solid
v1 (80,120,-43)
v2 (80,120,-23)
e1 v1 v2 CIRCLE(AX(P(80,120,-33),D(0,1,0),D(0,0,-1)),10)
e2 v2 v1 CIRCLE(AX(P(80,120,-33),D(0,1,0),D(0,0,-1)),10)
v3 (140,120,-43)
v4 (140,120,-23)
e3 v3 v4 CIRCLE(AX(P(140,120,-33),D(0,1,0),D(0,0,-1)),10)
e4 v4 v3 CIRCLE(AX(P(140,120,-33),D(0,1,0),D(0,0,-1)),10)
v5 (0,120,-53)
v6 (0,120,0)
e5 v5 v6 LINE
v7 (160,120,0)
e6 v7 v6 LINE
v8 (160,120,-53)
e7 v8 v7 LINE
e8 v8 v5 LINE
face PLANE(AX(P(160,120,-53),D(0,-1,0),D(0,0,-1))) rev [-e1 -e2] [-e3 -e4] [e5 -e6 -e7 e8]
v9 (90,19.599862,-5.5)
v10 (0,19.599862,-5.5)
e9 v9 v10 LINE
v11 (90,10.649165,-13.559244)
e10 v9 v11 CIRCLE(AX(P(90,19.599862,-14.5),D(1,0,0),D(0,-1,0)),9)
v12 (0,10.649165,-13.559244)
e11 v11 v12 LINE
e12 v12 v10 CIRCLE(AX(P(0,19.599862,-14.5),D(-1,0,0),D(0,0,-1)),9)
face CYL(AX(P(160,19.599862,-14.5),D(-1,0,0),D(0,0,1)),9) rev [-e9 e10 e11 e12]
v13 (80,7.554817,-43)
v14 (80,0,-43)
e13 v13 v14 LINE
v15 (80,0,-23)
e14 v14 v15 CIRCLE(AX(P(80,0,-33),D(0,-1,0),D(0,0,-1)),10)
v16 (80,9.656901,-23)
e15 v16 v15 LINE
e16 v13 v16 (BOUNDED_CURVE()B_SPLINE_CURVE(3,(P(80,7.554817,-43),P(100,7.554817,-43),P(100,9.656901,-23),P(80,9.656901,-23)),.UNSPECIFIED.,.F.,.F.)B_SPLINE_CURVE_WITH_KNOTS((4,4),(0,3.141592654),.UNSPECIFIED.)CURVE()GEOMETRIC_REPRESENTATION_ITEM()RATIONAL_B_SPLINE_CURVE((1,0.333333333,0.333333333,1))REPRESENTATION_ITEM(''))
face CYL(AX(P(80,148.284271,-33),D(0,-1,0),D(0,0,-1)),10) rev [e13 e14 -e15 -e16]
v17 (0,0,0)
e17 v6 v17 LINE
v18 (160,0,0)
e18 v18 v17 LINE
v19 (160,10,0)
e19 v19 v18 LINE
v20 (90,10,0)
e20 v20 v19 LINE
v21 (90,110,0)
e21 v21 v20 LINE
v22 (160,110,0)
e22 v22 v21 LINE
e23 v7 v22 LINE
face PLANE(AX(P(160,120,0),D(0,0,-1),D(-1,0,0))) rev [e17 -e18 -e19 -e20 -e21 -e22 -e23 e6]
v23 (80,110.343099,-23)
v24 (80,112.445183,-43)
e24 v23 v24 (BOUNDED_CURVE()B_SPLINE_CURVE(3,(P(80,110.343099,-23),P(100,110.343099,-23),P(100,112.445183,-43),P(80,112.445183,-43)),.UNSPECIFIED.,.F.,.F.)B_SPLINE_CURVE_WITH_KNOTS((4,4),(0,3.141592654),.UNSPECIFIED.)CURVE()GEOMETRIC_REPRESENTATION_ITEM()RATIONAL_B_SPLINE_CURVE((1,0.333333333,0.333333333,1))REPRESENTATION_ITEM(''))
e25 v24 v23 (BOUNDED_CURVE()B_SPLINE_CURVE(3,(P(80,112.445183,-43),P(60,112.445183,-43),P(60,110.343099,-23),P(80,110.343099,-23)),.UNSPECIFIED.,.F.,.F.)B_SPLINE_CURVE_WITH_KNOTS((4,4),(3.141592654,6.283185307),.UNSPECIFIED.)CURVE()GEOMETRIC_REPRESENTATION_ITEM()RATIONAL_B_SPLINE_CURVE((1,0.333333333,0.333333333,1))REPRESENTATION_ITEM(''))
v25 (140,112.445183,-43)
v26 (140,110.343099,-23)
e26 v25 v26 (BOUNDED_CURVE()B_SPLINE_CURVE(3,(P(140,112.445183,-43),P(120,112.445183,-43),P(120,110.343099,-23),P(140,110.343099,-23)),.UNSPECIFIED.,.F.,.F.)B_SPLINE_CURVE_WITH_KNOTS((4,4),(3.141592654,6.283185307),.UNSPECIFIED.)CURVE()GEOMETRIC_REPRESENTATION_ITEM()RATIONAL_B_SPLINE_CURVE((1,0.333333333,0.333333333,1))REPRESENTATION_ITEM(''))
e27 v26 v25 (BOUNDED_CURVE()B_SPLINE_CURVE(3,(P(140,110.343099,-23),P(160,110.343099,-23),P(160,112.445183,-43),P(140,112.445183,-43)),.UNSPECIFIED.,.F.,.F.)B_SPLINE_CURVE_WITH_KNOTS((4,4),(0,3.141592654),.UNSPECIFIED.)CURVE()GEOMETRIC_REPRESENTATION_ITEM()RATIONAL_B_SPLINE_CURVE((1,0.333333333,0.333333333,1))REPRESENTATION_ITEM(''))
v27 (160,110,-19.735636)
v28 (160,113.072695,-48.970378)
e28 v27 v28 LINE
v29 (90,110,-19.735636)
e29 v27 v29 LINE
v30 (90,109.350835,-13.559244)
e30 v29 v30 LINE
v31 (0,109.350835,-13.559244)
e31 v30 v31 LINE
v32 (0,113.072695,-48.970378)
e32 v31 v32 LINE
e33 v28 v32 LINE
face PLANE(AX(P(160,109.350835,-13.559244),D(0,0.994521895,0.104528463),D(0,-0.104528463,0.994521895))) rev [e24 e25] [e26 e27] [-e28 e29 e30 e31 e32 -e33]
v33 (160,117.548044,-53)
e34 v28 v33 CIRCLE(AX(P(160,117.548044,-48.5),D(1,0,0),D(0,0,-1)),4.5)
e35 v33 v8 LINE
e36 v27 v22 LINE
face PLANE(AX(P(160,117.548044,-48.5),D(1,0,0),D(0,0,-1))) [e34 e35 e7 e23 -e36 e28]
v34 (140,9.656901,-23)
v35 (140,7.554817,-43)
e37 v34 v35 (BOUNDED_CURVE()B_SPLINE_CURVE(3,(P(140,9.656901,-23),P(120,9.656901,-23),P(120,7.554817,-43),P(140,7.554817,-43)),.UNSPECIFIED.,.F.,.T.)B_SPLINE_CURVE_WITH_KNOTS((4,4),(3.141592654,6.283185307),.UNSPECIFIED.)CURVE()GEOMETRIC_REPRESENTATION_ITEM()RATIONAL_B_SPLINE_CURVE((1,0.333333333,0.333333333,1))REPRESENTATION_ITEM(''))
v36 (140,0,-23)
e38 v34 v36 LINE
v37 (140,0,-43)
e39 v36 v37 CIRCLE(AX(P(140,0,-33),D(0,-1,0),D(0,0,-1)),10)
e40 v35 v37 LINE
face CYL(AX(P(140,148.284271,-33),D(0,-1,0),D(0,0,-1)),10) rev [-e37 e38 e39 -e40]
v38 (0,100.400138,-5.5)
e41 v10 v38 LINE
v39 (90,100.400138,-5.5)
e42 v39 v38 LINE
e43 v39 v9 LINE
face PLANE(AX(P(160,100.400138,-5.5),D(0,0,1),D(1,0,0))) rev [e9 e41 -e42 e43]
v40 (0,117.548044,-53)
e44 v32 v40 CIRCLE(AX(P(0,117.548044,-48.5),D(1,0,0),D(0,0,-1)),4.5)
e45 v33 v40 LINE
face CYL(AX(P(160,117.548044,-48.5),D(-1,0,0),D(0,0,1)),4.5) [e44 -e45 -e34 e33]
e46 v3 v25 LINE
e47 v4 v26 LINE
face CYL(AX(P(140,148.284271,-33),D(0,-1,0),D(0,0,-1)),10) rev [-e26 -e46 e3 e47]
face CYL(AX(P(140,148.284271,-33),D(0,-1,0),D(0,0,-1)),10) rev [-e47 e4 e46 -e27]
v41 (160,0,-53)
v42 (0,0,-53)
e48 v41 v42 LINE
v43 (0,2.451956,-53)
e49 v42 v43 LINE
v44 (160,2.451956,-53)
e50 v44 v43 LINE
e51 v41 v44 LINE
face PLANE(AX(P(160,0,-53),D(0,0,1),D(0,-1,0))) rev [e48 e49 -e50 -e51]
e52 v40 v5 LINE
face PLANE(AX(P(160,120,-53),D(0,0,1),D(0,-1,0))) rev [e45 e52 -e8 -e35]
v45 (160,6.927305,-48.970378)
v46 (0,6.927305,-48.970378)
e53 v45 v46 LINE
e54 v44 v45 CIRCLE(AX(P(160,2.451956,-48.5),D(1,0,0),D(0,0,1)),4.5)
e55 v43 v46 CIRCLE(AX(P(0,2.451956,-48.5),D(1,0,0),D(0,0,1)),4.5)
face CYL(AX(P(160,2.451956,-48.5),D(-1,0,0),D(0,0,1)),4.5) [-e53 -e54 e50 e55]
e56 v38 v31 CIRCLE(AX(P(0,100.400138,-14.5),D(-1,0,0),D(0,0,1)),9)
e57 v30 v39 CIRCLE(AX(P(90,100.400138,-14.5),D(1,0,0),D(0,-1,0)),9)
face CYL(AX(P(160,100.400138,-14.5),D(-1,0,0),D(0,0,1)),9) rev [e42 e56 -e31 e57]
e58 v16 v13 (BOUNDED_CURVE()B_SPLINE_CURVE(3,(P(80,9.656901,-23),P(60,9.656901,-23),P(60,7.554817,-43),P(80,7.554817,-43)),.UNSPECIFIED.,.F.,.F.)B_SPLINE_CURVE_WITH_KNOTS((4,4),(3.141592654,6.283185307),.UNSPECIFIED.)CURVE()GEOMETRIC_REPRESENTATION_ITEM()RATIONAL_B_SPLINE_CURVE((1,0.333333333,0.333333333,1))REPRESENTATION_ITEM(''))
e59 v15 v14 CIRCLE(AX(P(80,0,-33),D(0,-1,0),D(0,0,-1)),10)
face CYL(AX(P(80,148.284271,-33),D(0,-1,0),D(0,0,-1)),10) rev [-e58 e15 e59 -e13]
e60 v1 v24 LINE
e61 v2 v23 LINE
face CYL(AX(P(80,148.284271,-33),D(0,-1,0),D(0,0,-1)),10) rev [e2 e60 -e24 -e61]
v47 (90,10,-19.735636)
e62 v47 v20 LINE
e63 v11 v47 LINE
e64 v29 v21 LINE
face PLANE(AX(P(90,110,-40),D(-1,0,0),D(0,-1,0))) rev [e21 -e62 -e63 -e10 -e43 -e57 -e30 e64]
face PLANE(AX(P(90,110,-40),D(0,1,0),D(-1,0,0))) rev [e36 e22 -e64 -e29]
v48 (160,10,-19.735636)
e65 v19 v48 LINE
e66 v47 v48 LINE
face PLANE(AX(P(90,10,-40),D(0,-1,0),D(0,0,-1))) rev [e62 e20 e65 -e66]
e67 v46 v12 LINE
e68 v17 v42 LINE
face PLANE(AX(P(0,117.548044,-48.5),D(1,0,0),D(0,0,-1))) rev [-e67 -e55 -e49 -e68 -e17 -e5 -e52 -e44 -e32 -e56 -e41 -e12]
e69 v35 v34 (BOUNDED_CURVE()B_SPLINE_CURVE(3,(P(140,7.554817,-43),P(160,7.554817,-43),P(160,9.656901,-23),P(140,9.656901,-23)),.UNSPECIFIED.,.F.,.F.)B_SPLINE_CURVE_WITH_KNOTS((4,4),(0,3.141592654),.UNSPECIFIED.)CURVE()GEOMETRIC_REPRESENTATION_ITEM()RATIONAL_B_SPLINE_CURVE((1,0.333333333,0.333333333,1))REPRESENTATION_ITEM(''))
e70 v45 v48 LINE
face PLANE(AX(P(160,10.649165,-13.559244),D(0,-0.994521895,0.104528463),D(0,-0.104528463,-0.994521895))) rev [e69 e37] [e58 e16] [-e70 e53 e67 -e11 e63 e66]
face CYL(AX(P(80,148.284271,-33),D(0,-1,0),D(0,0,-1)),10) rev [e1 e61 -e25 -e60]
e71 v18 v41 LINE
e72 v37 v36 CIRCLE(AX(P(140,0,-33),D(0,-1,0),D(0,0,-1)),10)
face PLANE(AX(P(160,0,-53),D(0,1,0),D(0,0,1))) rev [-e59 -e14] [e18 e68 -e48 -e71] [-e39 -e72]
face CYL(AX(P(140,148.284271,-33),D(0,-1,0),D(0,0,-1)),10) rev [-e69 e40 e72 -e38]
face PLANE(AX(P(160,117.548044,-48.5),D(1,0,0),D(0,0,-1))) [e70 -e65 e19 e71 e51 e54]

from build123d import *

# Parameters (mm, degrees)
C_CHANNEL_12_1_DEPTH = 160
SKETCH2_W            = 100
SKETCH2_H            = 100
CUT_EXTRUDE1_DEPTH   = 40
CUT_EXTRUDE2_REACH   = 208.903
SKETCH3_R            = 10


with BuildPart() as part:
    # Sketch11 → C-channel 12(1) (new body)
    with BuildSketch(Plane(origin=(0, 0, 0), x_dir=(0, 0, -1), z_dir=(1, 0, 0))):
        with BuildLine():
            Line((53, 120), (0, 120))
            Line((0, 120), (0, 0))
            Line((0, 0), (53, 0))
            Line((53, 0), (53, 2.451956213))
            ThreePointArc((53, 2.451956213), (51.844151715, 5.463043942), (48.970378085, 6.927304742))
            Line((48.970378085, 6.927304742), (13.559243831, 10.649164928))
            ThreePointArc((13.559243831, 10.649164928), (7.811696571, 13.577686529), (5.5, 19.599861986))
            Line((5.5, 19.599861986), (5.5, 100.400138014))
            ThreePointArc((5.5, 100.400138014), (7.811696571, 106.422313471), (13.559243831, 109.350835072))
            Line((13.559243831, 109.350835072), (48.970378085, 113.072695258))
            ThreePointArc((48.970378085, 113.072695258), (51.844151715, 114.536956058), (53, 117.548043787))
            Line((53, 117.548043787), (53, 120))
        make_face()
    extrude(amount=C_CHANNEL_12_1_DEPTH)

    # Sketch2 → Cut-Extrude1 (cut)
    with BuildSketch(Plane.XY):
        with Locations((140, 60)):
            Rectangle(SKETCH2_W, SKETCH2_H)
    extrude(amount=-CUT_EXTRUDE1_DEPTH, mode=Mode.SUBTRACT)

    # Cut-Extrude2: up to this face of the body (flat: up to its plane)
    cut_extrude2_end = Plane(part.part.faces().sort_by_distance((80, 120, -26.5))[0])
    # Sketch3 → Cut-Extrude2 (cut, up to the picked face)
    with BuildSketch(Plane.XZ, mode=Mode.PRIVATE) as cut_extrude2_sk1:
        with Locations(Location((140, -33, 0), (0, 0, 270))):
            Circle(SKETCH3_R)
    cut_extrude2_tool1 = split(extrude(cut_extrude2_sk1.sketch, amount=-CUT_EXTRUDE2_REACH, mode=Mode.PRIVATE), bisect_by=cut_extrude2_end, keep=Keep.BOTH, mode=Mode.PRIVATE)
    # Sketch3 → Cut-Extrude2 (cut, up to the picked face)
    with BuildSketch(Plane.XZ, mode=Mode.PRIVATE) as cut_extrude2_sk2:
        with Locations(Location((80, -33, 0), (0, 0, 270))):
            Circle(SKETCH3_R)
    cut_extrude2_tool2 = split(extrude(cut_extrude2_sk2.sketch, amount=-CUT_EXTRUDE2_REACH, mode=Mode.PRIVATE), bisect_by=cut_extrude2_end, keep=Keep.BOTH, mode=Mode.PRIVATE)
    add(cut_extrude2_tool1.solids().sort_by(Axis((140, 0, -33), (0, 1, 0)))[0], mode=Mode.SUBTRACT)
    add(cut_extrude2_tool2.solids().sort_by(Axis((80, 0, -33), (0, 1, 0)))[0], mode=Mode.SUBTRACT)


solid = part.part
